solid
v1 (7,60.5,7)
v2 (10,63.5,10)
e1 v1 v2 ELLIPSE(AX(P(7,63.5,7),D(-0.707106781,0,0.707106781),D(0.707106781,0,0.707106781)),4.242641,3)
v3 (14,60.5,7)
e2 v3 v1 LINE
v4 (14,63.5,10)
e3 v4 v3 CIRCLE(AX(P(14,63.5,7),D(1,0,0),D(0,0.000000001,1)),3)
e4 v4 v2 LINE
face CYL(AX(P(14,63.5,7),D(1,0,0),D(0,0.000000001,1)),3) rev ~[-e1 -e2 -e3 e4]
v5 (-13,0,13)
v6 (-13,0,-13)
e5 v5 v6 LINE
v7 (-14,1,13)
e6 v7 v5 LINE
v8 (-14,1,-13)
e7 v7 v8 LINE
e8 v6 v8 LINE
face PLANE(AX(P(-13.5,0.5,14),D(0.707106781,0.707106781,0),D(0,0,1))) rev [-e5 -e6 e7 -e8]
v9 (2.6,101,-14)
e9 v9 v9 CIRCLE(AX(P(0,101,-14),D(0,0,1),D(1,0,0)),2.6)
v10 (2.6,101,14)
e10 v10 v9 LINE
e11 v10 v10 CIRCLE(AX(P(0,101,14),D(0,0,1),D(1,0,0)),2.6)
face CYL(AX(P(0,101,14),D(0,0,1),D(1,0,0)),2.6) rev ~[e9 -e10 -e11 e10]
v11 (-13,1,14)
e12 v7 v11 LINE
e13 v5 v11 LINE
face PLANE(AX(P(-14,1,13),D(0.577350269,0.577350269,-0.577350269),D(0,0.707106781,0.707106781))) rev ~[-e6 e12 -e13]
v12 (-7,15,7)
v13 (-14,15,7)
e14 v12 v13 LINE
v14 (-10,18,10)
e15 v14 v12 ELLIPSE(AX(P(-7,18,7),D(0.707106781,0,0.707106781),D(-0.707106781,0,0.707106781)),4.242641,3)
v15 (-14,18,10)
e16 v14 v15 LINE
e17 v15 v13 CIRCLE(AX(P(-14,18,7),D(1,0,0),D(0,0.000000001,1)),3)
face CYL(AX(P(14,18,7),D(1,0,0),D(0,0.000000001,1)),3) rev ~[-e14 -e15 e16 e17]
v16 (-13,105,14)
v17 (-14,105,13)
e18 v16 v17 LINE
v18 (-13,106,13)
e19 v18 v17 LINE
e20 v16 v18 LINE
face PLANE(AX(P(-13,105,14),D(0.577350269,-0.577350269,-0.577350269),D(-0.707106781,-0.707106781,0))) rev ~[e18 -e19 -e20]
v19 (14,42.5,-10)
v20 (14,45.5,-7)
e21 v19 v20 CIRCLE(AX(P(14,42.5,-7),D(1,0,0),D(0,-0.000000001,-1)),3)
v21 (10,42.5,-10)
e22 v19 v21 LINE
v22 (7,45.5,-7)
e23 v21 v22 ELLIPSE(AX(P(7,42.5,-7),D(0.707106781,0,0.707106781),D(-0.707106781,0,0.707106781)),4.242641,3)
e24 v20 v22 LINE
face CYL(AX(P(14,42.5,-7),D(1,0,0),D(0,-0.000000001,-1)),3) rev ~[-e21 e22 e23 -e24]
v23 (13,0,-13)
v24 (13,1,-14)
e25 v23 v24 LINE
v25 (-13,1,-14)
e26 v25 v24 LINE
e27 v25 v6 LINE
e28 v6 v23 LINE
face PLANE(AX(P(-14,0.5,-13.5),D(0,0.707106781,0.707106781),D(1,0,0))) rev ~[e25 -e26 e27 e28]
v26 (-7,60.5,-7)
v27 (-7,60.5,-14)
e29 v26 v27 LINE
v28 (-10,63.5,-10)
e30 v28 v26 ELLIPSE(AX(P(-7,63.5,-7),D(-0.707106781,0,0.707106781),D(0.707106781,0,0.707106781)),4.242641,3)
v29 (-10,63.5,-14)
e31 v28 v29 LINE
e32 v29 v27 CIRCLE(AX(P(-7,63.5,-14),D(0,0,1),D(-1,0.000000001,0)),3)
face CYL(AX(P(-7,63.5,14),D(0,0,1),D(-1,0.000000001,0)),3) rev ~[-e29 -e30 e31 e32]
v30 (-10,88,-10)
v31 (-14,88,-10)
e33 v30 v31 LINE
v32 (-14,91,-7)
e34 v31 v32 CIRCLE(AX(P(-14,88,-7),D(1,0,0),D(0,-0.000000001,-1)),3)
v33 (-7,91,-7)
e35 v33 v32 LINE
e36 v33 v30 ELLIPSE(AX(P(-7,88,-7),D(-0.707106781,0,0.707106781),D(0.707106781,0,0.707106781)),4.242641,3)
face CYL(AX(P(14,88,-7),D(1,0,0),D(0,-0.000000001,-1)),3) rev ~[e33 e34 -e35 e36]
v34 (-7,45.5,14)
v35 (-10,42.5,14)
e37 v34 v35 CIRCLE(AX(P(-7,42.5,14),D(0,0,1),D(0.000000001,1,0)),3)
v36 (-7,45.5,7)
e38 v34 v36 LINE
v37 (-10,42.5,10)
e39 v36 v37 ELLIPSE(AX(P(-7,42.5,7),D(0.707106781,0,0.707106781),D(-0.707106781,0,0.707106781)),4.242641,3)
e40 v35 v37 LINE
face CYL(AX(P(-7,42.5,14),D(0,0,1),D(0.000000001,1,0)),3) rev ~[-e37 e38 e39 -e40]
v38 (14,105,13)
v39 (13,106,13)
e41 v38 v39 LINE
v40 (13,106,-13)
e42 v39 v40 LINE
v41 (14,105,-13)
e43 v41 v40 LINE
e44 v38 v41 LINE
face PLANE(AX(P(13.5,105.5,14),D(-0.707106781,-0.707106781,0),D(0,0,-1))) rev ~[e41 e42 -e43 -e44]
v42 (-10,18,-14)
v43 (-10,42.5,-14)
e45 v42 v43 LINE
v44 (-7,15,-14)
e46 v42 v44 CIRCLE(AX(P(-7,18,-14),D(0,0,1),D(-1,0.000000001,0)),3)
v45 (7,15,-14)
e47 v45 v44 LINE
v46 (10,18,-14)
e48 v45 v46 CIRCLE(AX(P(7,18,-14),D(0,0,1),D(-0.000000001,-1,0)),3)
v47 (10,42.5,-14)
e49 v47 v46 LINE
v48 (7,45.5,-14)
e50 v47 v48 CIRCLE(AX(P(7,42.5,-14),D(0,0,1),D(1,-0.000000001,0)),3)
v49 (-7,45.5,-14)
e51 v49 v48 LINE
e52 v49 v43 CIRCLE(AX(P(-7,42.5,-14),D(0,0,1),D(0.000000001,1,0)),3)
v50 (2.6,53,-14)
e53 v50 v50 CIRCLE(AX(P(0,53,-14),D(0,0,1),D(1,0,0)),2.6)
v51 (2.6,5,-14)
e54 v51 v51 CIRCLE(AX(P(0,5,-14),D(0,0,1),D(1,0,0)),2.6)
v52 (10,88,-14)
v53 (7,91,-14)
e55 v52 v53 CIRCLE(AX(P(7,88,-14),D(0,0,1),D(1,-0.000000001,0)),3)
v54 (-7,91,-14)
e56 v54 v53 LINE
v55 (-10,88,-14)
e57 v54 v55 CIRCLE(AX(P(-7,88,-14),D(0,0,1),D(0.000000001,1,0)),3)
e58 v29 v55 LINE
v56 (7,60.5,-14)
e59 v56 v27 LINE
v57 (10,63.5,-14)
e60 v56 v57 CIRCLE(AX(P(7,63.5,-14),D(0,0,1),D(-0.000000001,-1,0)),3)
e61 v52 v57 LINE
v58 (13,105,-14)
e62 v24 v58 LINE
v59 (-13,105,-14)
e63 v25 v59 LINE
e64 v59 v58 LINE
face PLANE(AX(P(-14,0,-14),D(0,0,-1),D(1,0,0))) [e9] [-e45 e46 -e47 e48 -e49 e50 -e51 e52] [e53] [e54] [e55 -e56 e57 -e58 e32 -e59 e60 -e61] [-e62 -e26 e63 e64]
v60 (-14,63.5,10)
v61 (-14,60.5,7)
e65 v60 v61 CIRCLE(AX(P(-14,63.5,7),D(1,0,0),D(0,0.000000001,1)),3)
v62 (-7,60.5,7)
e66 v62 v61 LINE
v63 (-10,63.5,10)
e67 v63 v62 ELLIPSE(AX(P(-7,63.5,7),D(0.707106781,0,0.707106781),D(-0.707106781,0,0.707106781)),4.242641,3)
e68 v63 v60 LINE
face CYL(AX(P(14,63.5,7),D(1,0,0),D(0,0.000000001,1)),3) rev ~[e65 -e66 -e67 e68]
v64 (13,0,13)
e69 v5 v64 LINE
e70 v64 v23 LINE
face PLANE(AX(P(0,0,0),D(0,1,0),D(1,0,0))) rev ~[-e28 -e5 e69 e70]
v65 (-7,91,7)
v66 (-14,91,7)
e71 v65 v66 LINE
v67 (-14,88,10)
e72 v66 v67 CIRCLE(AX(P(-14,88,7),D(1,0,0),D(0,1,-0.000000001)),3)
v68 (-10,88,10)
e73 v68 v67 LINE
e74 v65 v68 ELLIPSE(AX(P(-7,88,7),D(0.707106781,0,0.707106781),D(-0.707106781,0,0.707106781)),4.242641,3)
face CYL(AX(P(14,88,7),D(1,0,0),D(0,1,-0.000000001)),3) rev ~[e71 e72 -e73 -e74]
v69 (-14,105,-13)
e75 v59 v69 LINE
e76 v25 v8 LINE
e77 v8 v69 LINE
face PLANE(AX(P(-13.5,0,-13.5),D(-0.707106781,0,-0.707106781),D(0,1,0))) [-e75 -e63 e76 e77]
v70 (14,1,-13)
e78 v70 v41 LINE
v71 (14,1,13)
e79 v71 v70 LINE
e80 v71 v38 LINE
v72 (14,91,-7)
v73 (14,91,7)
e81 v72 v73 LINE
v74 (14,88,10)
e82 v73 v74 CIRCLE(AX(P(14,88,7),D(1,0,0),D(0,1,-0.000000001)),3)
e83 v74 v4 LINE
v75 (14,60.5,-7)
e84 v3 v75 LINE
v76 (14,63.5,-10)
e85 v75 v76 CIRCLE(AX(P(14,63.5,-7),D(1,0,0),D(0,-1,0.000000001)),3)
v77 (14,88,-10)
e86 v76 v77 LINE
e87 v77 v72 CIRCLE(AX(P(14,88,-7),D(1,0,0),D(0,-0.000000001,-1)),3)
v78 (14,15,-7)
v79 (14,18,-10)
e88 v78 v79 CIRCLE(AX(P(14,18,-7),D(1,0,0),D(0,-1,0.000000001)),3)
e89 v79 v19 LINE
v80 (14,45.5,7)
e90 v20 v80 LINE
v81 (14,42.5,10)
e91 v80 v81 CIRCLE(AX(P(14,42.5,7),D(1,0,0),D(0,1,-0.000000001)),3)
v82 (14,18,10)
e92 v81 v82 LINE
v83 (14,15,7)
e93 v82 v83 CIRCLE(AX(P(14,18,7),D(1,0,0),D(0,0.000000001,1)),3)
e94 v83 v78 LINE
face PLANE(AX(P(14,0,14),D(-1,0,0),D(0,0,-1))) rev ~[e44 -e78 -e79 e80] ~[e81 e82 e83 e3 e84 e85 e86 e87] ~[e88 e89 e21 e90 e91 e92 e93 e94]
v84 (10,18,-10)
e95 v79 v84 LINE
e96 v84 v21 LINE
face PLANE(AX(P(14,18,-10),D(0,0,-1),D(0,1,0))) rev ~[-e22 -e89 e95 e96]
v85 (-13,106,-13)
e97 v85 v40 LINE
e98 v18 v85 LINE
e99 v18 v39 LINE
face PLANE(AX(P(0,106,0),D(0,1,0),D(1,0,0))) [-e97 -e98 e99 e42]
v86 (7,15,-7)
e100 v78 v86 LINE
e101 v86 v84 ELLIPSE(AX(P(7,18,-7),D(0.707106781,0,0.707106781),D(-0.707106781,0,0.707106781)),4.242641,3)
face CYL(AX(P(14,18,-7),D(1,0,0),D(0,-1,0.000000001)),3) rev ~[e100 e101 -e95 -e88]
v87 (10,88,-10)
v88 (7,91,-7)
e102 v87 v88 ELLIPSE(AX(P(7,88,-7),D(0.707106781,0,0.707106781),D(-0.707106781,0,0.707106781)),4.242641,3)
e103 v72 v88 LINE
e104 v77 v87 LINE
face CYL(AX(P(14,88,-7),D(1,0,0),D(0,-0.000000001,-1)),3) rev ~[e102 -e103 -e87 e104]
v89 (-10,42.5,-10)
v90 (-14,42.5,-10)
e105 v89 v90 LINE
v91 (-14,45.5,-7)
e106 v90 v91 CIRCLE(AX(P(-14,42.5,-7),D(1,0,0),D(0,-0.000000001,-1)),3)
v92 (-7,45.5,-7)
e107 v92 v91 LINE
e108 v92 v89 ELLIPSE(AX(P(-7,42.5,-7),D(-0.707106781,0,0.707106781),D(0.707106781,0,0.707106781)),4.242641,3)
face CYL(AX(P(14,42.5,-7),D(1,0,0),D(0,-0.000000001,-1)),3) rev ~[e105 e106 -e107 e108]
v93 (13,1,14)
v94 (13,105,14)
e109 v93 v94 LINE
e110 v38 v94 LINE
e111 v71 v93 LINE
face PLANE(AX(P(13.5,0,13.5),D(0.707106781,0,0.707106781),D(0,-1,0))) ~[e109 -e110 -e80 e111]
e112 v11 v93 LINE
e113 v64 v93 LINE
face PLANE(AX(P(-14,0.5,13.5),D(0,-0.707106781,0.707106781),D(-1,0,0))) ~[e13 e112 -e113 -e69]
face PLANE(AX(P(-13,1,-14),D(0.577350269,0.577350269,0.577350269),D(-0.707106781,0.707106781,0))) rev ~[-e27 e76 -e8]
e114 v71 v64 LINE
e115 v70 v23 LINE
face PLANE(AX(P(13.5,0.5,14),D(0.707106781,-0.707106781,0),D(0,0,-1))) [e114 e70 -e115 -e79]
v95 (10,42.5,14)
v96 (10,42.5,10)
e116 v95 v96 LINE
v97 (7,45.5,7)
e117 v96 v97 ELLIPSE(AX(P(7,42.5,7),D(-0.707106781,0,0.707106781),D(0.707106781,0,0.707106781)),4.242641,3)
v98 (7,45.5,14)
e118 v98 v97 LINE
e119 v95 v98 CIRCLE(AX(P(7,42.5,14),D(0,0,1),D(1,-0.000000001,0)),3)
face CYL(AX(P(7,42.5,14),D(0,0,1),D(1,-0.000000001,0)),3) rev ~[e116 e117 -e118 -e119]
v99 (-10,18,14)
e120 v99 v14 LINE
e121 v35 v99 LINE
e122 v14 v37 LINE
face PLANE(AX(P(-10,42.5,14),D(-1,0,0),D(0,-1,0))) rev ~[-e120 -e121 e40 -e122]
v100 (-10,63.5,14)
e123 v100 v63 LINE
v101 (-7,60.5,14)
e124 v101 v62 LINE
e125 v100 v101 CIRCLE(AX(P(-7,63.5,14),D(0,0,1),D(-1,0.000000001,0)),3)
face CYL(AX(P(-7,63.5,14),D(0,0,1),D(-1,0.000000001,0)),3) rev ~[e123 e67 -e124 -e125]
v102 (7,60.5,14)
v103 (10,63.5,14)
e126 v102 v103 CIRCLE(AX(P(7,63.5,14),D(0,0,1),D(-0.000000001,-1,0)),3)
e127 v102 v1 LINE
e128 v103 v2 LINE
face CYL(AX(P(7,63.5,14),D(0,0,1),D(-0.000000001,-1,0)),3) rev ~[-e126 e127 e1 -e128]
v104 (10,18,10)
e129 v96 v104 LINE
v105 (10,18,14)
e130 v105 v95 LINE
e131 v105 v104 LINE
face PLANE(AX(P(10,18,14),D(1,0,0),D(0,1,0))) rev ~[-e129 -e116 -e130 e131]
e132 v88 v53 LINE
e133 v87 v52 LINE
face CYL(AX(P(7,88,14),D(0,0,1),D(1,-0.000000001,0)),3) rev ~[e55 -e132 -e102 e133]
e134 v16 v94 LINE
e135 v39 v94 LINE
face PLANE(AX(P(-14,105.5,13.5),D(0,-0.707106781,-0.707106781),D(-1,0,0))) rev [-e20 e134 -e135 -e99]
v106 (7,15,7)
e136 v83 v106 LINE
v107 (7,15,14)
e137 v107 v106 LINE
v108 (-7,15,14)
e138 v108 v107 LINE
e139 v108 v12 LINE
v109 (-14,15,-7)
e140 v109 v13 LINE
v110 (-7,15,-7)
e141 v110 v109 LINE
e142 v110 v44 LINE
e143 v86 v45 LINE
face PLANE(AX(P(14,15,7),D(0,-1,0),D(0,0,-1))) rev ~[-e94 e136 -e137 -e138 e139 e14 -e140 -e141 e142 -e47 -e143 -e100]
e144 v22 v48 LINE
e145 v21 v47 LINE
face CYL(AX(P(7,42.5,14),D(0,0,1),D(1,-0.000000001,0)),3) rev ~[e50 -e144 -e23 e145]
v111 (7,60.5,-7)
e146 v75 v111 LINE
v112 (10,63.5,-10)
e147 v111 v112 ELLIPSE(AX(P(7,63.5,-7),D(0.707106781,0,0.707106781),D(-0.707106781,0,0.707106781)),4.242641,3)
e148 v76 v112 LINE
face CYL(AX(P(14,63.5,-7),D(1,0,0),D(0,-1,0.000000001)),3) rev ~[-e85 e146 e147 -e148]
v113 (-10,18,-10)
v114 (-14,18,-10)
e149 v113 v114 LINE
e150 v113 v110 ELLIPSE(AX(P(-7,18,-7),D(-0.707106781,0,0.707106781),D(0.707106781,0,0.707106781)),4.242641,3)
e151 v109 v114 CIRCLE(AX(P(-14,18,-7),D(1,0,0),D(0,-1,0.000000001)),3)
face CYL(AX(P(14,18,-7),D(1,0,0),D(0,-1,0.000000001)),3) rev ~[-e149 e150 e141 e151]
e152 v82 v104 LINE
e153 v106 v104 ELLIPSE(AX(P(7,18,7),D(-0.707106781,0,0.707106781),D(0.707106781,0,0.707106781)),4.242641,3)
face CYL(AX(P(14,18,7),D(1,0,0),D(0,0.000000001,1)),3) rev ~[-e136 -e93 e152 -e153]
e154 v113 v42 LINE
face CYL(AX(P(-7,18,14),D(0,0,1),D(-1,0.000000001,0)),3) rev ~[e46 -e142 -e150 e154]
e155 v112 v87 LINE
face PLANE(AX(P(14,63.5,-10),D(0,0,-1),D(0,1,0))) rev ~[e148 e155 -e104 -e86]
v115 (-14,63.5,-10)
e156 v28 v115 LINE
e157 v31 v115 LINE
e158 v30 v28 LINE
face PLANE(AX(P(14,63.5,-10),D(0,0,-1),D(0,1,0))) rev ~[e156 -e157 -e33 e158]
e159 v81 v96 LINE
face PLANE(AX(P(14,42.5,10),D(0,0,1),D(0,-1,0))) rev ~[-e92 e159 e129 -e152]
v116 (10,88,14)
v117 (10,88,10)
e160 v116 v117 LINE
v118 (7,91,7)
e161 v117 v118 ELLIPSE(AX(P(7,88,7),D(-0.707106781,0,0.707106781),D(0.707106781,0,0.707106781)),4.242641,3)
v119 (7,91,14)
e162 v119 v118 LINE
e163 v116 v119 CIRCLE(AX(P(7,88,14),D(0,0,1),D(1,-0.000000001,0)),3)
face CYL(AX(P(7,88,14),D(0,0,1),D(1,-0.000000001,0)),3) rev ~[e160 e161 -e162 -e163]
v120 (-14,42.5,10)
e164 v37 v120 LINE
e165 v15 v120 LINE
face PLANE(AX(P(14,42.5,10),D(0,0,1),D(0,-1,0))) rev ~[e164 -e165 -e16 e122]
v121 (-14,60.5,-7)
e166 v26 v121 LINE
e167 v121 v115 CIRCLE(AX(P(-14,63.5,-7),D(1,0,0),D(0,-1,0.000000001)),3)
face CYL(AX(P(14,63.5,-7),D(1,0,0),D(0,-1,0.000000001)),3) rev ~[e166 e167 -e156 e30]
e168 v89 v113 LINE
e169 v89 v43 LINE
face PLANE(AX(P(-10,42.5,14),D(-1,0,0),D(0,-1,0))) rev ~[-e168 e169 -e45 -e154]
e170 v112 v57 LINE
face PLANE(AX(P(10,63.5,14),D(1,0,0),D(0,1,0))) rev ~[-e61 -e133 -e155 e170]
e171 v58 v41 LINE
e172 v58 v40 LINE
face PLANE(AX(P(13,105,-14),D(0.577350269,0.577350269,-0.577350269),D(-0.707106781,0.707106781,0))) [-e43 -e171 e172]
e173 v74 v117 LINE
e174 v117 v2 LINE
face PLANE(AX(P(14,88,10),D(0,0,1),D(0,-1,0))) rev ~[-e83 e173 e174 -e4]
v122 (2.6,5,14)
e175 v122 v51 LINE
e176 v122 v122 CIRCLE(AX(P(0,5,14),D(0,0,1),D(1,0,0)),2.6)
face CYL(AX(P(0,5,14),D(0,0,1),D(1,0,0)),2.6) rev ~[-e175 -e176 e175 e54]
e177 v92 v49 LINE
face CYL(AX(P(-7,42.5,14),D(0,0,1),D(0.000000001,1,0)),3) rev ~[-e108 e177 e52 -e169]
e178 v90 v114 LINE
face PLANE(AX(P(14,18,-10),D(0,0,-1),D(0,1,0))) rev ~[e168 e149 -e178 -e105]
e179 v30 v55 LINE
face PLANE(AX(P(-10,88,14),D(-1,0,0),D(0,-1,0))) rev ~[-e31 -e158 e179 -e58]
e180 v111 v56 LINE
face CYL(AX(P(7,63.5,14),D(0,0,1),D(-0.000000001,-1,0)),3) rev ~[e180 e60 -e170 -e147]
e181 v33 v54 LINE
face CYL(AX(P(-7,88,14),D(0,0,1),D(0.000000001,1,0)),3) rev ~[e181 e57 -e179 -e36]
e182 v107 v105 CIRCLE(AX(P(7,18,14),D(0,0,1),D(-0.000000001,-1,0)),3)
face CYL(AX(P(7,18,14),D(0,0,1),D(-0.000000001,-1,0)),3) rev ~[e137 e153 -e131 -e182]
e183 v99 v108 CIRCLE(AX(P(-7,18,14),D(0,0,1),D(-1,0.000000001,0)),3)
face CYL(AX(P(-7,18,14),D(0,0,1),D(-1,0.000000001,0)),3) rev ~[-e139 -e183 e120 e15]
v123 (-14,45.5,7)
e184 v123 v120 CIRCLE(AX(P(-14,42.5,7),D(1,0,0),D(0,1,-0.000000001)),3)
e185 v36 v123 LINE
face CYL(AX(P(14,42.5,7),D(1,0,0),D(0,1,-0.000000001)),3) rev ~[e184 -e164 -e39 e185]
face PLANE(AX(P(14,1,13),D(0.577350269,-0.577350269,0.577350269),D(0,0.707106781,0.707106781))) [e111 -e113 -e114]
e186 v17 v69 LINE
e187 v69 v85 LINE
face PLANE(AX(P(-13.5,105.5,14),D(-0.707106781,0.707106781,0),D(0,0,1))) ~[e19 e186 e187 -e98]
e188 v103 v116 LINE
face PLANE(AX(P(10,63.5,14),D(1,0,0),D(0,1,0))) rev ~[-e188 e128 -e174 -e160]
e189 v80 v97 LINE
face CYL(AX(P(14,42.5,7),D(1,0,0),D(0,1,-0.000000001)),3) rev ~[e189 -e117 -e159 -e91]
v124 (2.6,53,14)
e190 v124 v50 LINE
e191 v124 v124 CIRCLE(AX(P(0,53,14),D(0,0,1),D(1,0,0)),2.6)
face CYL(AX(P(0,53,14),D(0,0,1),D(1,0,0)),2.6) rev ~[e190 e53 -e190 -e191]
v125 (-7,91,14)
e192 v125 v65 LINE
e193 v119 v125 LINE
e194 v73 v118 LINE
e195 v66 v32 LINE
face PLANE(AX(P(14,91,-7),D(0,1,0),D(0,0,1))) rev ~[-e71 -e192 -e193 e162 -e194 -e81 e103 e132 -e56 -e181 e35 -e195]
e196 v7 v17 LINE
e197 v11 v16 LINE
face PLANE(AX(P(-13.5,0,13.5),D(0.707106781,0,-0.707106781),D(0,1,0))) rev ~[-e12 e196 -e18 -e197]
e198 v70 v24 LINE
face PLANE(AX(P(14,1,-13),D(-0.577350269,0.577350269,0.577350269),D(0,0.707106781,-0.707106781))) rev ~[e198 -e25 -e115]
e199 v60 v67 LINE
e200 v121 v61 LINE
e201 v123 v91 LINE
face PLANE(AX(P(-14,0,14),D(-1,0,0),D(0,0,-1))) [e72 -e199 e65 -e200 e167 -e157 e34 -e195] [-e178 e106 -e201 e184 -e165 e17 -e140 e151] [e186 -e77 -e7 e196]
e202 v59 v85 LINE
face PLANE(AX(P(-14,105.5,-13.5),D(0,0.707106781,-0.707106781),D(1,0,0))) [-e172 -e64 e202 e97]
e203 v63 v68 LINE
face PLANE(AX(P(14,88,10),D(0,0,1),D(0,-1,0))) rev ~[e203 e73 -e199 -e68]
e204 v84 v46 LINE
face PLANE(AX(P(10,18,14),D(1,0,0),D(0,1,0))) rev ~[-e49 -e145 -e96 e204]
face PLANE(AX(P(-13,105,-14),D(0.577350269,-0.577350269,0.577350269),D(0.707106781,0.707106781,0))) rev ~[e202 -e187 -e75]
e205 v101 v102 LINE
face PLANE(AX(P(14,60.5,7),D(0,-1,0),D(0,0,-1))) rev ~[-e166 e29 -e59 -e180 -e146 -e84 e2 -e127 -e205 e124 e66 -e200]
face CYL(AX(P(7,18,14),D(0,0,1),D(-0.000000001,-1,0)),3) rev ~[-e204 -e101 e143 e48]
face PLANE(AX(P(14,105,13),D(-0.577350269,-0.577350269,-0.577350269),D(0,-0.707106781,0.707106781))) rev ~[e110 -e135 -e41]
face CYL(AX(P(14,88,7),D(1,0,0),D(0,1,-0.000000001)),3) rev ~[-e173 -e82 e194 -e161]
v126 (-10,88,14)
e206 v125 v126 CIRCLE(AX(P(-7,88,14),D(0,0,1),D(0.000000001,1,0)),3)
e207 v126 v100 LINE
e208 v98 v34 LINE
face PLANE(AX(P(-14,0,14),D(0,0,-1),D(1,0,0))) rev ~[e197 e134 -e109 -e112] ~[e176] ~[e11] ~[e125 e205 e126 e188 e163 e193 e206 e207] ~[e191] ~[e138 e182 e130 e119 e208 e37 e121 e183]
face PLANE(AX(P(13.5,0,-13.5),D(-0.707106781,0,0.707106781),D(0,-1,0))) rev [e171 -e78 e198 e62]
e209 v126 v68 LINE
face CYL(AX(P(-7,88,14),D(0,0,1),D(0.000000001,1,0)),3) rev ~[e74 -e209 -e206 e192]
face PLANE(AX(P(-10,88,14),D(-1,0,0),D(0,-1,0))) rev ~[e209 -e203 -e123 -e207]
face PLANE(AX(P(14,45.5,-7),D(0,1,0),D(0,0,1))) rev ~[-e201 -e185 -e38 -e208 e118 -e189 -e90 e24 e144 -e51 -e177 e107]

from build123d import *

# Parameters (mm, degrees)
SKETCH_1_W          = 28
SKETCH_1_H          = 28
EXTRUDE_1_DEPTH     = 106
SKETCH_2_R          = 2.6
CUT_EXTRUDE_1_DEPTH = 111.526015037
CUT_EXTRUDE_2_DEPTH = 111.526015037
CHAMFER_1_SIZE      = 1


with BuildPart() as part:
    # 草图1 → 凸台-拉伸1 (new body)
    with BuildSketch(Plane(origin=(0, 0, 0), x_dir=(1, 0, 0), z_dir=(0, 1, 0))):
        Rectangle(SKETCH_1_W, SKETCH_1_H)
    extrude(amount=EXTRUDE_1_DEPTH)

    # 草图2 → 切除-拉伸1 (cut, through all)
    with BuildSketch(Plane.XY.offset(14)):
        with Locations((0, 101)):
            Circle(SKETCH_2_R)
        with Locations((0, 53)):
            Circle(SKETCH_2_R)
        with Locations((0, 5)):
            Circle(SKETCH_2_R)
        with BuildLine():
            Line((-7, 60.5), (7, 60.5))
            ThreePointArc((7, 60.5), (9.121320344, 61.378679656), (10, 63.5))
            Line((10, 63.5), (10, 88))
            ThreePointArc((10, 88), (9.121320344, 90.121320344), (7, 91))
            Line((7, 91), (-7, 91))
            ThreePointArc((-7, 91), (-9.121320344, 90.121320344), (-10, 88))
            Line((-10, 88), (-10, 63.5))
            ThreePointArc((-10, 63.5), (-9.121320344, 61.378679656), (-7, 60.5))
        make_face()
        with BuildLine():
            Line((-7, 15), (7, 15))
            ThreePointArc((7, 15), (9.121320344, 15.878679656), (10, 18))
            Line((10, 18), (10, 42.5))
            ThreePointArc((10, 42.5), (9.121320344, 44.621320344), (7, 45.5))
            Line((7, 45.5), (-7, 45.5))
            ThreePointArc((-7, 45.5), (-9.121320344, 44.621320344), (-10, 42.5))
            Line((-10, 42.5), (-10, 18))
            ThreePointArc((-10, 18), (-9.121320344, 15.878679656), (-7, 15))
        make_face()
    extrude(amount=-CUT_EXTRUDE_1_DEPTH, mode=Mode.SUBTRACT)

    # 草图3 → 切除-拉伸2 (cut, through all)
    with BuildSketch(Plane(origin=(14, 0, 0), x_dir=(0, 0, -1), z_dir=(1, 0, 0))):
        with BuildLine():
            Line((-7, 60.5), (7, 60.5))
            ThreePointArc((7, 60.5), (9.121320344, 61.378679656), (10, 63.5))
            Line((10, 63.5), (10, 88))
            ThreePointArc((10, 88), (9.121320344, 90.121320344), (7, 91))
            Line((7, 91), (-7, 91))
            ThreePointArc((-7, 91), (-9.121320344, 90.121320344), (-10, 88))
            Line((-10, 88), (-10, 63.5))
            ThreePointArc((-10, 63.5), (-9.121320344, 61.378679656), (-7, 60.5))
        make_face()
        with BuildLine():
            Line((-7, 15), (7, 15))
            ThreePointArc((7, 15), (9.121320344, 15.878679656), (10, 18))
            Line((10, 18), (10, 42.5))
            ThreePointArc((10, 42.5), (9.121320344, 44.621320344), (7, 45.5))
            Line((7, 45.5), (-7, 45.5))
            ThreePointArc((-7, 45.5), (-9.121320344, 44.621320344), (-10, 42.5))
            Line((-10, 42.5), (-10, 18))
            ThreePointArc((-10, 18), (-9.121320344, 15.878679656), (-7, 15))
        make_face()
    extrude(amount=-CUT_EXTRUDE_2_DEPTH, mode=Mode.SUBTRACT)

    # 倒角1
    chamfer_1_edges = [part.edges().sort_by_distance(p)[0] for p in [
        (-14, 106, 0),
        (0, 106, 14),
        (14, 106, 0),
        (0, 0, 14),
        (-14, 0, 0),
        (0, 0, -14),
        (14, 0, 0),
        (14, 53, 14),
        (-14, 53, 14),
        (-14, 53, -14),
        (14, 53, -14),
        (0, 106, -14),
    ]]
    chamfer(chamfer_1_edges, length=CHAMFER_1_SIZE)


solid = part.part
